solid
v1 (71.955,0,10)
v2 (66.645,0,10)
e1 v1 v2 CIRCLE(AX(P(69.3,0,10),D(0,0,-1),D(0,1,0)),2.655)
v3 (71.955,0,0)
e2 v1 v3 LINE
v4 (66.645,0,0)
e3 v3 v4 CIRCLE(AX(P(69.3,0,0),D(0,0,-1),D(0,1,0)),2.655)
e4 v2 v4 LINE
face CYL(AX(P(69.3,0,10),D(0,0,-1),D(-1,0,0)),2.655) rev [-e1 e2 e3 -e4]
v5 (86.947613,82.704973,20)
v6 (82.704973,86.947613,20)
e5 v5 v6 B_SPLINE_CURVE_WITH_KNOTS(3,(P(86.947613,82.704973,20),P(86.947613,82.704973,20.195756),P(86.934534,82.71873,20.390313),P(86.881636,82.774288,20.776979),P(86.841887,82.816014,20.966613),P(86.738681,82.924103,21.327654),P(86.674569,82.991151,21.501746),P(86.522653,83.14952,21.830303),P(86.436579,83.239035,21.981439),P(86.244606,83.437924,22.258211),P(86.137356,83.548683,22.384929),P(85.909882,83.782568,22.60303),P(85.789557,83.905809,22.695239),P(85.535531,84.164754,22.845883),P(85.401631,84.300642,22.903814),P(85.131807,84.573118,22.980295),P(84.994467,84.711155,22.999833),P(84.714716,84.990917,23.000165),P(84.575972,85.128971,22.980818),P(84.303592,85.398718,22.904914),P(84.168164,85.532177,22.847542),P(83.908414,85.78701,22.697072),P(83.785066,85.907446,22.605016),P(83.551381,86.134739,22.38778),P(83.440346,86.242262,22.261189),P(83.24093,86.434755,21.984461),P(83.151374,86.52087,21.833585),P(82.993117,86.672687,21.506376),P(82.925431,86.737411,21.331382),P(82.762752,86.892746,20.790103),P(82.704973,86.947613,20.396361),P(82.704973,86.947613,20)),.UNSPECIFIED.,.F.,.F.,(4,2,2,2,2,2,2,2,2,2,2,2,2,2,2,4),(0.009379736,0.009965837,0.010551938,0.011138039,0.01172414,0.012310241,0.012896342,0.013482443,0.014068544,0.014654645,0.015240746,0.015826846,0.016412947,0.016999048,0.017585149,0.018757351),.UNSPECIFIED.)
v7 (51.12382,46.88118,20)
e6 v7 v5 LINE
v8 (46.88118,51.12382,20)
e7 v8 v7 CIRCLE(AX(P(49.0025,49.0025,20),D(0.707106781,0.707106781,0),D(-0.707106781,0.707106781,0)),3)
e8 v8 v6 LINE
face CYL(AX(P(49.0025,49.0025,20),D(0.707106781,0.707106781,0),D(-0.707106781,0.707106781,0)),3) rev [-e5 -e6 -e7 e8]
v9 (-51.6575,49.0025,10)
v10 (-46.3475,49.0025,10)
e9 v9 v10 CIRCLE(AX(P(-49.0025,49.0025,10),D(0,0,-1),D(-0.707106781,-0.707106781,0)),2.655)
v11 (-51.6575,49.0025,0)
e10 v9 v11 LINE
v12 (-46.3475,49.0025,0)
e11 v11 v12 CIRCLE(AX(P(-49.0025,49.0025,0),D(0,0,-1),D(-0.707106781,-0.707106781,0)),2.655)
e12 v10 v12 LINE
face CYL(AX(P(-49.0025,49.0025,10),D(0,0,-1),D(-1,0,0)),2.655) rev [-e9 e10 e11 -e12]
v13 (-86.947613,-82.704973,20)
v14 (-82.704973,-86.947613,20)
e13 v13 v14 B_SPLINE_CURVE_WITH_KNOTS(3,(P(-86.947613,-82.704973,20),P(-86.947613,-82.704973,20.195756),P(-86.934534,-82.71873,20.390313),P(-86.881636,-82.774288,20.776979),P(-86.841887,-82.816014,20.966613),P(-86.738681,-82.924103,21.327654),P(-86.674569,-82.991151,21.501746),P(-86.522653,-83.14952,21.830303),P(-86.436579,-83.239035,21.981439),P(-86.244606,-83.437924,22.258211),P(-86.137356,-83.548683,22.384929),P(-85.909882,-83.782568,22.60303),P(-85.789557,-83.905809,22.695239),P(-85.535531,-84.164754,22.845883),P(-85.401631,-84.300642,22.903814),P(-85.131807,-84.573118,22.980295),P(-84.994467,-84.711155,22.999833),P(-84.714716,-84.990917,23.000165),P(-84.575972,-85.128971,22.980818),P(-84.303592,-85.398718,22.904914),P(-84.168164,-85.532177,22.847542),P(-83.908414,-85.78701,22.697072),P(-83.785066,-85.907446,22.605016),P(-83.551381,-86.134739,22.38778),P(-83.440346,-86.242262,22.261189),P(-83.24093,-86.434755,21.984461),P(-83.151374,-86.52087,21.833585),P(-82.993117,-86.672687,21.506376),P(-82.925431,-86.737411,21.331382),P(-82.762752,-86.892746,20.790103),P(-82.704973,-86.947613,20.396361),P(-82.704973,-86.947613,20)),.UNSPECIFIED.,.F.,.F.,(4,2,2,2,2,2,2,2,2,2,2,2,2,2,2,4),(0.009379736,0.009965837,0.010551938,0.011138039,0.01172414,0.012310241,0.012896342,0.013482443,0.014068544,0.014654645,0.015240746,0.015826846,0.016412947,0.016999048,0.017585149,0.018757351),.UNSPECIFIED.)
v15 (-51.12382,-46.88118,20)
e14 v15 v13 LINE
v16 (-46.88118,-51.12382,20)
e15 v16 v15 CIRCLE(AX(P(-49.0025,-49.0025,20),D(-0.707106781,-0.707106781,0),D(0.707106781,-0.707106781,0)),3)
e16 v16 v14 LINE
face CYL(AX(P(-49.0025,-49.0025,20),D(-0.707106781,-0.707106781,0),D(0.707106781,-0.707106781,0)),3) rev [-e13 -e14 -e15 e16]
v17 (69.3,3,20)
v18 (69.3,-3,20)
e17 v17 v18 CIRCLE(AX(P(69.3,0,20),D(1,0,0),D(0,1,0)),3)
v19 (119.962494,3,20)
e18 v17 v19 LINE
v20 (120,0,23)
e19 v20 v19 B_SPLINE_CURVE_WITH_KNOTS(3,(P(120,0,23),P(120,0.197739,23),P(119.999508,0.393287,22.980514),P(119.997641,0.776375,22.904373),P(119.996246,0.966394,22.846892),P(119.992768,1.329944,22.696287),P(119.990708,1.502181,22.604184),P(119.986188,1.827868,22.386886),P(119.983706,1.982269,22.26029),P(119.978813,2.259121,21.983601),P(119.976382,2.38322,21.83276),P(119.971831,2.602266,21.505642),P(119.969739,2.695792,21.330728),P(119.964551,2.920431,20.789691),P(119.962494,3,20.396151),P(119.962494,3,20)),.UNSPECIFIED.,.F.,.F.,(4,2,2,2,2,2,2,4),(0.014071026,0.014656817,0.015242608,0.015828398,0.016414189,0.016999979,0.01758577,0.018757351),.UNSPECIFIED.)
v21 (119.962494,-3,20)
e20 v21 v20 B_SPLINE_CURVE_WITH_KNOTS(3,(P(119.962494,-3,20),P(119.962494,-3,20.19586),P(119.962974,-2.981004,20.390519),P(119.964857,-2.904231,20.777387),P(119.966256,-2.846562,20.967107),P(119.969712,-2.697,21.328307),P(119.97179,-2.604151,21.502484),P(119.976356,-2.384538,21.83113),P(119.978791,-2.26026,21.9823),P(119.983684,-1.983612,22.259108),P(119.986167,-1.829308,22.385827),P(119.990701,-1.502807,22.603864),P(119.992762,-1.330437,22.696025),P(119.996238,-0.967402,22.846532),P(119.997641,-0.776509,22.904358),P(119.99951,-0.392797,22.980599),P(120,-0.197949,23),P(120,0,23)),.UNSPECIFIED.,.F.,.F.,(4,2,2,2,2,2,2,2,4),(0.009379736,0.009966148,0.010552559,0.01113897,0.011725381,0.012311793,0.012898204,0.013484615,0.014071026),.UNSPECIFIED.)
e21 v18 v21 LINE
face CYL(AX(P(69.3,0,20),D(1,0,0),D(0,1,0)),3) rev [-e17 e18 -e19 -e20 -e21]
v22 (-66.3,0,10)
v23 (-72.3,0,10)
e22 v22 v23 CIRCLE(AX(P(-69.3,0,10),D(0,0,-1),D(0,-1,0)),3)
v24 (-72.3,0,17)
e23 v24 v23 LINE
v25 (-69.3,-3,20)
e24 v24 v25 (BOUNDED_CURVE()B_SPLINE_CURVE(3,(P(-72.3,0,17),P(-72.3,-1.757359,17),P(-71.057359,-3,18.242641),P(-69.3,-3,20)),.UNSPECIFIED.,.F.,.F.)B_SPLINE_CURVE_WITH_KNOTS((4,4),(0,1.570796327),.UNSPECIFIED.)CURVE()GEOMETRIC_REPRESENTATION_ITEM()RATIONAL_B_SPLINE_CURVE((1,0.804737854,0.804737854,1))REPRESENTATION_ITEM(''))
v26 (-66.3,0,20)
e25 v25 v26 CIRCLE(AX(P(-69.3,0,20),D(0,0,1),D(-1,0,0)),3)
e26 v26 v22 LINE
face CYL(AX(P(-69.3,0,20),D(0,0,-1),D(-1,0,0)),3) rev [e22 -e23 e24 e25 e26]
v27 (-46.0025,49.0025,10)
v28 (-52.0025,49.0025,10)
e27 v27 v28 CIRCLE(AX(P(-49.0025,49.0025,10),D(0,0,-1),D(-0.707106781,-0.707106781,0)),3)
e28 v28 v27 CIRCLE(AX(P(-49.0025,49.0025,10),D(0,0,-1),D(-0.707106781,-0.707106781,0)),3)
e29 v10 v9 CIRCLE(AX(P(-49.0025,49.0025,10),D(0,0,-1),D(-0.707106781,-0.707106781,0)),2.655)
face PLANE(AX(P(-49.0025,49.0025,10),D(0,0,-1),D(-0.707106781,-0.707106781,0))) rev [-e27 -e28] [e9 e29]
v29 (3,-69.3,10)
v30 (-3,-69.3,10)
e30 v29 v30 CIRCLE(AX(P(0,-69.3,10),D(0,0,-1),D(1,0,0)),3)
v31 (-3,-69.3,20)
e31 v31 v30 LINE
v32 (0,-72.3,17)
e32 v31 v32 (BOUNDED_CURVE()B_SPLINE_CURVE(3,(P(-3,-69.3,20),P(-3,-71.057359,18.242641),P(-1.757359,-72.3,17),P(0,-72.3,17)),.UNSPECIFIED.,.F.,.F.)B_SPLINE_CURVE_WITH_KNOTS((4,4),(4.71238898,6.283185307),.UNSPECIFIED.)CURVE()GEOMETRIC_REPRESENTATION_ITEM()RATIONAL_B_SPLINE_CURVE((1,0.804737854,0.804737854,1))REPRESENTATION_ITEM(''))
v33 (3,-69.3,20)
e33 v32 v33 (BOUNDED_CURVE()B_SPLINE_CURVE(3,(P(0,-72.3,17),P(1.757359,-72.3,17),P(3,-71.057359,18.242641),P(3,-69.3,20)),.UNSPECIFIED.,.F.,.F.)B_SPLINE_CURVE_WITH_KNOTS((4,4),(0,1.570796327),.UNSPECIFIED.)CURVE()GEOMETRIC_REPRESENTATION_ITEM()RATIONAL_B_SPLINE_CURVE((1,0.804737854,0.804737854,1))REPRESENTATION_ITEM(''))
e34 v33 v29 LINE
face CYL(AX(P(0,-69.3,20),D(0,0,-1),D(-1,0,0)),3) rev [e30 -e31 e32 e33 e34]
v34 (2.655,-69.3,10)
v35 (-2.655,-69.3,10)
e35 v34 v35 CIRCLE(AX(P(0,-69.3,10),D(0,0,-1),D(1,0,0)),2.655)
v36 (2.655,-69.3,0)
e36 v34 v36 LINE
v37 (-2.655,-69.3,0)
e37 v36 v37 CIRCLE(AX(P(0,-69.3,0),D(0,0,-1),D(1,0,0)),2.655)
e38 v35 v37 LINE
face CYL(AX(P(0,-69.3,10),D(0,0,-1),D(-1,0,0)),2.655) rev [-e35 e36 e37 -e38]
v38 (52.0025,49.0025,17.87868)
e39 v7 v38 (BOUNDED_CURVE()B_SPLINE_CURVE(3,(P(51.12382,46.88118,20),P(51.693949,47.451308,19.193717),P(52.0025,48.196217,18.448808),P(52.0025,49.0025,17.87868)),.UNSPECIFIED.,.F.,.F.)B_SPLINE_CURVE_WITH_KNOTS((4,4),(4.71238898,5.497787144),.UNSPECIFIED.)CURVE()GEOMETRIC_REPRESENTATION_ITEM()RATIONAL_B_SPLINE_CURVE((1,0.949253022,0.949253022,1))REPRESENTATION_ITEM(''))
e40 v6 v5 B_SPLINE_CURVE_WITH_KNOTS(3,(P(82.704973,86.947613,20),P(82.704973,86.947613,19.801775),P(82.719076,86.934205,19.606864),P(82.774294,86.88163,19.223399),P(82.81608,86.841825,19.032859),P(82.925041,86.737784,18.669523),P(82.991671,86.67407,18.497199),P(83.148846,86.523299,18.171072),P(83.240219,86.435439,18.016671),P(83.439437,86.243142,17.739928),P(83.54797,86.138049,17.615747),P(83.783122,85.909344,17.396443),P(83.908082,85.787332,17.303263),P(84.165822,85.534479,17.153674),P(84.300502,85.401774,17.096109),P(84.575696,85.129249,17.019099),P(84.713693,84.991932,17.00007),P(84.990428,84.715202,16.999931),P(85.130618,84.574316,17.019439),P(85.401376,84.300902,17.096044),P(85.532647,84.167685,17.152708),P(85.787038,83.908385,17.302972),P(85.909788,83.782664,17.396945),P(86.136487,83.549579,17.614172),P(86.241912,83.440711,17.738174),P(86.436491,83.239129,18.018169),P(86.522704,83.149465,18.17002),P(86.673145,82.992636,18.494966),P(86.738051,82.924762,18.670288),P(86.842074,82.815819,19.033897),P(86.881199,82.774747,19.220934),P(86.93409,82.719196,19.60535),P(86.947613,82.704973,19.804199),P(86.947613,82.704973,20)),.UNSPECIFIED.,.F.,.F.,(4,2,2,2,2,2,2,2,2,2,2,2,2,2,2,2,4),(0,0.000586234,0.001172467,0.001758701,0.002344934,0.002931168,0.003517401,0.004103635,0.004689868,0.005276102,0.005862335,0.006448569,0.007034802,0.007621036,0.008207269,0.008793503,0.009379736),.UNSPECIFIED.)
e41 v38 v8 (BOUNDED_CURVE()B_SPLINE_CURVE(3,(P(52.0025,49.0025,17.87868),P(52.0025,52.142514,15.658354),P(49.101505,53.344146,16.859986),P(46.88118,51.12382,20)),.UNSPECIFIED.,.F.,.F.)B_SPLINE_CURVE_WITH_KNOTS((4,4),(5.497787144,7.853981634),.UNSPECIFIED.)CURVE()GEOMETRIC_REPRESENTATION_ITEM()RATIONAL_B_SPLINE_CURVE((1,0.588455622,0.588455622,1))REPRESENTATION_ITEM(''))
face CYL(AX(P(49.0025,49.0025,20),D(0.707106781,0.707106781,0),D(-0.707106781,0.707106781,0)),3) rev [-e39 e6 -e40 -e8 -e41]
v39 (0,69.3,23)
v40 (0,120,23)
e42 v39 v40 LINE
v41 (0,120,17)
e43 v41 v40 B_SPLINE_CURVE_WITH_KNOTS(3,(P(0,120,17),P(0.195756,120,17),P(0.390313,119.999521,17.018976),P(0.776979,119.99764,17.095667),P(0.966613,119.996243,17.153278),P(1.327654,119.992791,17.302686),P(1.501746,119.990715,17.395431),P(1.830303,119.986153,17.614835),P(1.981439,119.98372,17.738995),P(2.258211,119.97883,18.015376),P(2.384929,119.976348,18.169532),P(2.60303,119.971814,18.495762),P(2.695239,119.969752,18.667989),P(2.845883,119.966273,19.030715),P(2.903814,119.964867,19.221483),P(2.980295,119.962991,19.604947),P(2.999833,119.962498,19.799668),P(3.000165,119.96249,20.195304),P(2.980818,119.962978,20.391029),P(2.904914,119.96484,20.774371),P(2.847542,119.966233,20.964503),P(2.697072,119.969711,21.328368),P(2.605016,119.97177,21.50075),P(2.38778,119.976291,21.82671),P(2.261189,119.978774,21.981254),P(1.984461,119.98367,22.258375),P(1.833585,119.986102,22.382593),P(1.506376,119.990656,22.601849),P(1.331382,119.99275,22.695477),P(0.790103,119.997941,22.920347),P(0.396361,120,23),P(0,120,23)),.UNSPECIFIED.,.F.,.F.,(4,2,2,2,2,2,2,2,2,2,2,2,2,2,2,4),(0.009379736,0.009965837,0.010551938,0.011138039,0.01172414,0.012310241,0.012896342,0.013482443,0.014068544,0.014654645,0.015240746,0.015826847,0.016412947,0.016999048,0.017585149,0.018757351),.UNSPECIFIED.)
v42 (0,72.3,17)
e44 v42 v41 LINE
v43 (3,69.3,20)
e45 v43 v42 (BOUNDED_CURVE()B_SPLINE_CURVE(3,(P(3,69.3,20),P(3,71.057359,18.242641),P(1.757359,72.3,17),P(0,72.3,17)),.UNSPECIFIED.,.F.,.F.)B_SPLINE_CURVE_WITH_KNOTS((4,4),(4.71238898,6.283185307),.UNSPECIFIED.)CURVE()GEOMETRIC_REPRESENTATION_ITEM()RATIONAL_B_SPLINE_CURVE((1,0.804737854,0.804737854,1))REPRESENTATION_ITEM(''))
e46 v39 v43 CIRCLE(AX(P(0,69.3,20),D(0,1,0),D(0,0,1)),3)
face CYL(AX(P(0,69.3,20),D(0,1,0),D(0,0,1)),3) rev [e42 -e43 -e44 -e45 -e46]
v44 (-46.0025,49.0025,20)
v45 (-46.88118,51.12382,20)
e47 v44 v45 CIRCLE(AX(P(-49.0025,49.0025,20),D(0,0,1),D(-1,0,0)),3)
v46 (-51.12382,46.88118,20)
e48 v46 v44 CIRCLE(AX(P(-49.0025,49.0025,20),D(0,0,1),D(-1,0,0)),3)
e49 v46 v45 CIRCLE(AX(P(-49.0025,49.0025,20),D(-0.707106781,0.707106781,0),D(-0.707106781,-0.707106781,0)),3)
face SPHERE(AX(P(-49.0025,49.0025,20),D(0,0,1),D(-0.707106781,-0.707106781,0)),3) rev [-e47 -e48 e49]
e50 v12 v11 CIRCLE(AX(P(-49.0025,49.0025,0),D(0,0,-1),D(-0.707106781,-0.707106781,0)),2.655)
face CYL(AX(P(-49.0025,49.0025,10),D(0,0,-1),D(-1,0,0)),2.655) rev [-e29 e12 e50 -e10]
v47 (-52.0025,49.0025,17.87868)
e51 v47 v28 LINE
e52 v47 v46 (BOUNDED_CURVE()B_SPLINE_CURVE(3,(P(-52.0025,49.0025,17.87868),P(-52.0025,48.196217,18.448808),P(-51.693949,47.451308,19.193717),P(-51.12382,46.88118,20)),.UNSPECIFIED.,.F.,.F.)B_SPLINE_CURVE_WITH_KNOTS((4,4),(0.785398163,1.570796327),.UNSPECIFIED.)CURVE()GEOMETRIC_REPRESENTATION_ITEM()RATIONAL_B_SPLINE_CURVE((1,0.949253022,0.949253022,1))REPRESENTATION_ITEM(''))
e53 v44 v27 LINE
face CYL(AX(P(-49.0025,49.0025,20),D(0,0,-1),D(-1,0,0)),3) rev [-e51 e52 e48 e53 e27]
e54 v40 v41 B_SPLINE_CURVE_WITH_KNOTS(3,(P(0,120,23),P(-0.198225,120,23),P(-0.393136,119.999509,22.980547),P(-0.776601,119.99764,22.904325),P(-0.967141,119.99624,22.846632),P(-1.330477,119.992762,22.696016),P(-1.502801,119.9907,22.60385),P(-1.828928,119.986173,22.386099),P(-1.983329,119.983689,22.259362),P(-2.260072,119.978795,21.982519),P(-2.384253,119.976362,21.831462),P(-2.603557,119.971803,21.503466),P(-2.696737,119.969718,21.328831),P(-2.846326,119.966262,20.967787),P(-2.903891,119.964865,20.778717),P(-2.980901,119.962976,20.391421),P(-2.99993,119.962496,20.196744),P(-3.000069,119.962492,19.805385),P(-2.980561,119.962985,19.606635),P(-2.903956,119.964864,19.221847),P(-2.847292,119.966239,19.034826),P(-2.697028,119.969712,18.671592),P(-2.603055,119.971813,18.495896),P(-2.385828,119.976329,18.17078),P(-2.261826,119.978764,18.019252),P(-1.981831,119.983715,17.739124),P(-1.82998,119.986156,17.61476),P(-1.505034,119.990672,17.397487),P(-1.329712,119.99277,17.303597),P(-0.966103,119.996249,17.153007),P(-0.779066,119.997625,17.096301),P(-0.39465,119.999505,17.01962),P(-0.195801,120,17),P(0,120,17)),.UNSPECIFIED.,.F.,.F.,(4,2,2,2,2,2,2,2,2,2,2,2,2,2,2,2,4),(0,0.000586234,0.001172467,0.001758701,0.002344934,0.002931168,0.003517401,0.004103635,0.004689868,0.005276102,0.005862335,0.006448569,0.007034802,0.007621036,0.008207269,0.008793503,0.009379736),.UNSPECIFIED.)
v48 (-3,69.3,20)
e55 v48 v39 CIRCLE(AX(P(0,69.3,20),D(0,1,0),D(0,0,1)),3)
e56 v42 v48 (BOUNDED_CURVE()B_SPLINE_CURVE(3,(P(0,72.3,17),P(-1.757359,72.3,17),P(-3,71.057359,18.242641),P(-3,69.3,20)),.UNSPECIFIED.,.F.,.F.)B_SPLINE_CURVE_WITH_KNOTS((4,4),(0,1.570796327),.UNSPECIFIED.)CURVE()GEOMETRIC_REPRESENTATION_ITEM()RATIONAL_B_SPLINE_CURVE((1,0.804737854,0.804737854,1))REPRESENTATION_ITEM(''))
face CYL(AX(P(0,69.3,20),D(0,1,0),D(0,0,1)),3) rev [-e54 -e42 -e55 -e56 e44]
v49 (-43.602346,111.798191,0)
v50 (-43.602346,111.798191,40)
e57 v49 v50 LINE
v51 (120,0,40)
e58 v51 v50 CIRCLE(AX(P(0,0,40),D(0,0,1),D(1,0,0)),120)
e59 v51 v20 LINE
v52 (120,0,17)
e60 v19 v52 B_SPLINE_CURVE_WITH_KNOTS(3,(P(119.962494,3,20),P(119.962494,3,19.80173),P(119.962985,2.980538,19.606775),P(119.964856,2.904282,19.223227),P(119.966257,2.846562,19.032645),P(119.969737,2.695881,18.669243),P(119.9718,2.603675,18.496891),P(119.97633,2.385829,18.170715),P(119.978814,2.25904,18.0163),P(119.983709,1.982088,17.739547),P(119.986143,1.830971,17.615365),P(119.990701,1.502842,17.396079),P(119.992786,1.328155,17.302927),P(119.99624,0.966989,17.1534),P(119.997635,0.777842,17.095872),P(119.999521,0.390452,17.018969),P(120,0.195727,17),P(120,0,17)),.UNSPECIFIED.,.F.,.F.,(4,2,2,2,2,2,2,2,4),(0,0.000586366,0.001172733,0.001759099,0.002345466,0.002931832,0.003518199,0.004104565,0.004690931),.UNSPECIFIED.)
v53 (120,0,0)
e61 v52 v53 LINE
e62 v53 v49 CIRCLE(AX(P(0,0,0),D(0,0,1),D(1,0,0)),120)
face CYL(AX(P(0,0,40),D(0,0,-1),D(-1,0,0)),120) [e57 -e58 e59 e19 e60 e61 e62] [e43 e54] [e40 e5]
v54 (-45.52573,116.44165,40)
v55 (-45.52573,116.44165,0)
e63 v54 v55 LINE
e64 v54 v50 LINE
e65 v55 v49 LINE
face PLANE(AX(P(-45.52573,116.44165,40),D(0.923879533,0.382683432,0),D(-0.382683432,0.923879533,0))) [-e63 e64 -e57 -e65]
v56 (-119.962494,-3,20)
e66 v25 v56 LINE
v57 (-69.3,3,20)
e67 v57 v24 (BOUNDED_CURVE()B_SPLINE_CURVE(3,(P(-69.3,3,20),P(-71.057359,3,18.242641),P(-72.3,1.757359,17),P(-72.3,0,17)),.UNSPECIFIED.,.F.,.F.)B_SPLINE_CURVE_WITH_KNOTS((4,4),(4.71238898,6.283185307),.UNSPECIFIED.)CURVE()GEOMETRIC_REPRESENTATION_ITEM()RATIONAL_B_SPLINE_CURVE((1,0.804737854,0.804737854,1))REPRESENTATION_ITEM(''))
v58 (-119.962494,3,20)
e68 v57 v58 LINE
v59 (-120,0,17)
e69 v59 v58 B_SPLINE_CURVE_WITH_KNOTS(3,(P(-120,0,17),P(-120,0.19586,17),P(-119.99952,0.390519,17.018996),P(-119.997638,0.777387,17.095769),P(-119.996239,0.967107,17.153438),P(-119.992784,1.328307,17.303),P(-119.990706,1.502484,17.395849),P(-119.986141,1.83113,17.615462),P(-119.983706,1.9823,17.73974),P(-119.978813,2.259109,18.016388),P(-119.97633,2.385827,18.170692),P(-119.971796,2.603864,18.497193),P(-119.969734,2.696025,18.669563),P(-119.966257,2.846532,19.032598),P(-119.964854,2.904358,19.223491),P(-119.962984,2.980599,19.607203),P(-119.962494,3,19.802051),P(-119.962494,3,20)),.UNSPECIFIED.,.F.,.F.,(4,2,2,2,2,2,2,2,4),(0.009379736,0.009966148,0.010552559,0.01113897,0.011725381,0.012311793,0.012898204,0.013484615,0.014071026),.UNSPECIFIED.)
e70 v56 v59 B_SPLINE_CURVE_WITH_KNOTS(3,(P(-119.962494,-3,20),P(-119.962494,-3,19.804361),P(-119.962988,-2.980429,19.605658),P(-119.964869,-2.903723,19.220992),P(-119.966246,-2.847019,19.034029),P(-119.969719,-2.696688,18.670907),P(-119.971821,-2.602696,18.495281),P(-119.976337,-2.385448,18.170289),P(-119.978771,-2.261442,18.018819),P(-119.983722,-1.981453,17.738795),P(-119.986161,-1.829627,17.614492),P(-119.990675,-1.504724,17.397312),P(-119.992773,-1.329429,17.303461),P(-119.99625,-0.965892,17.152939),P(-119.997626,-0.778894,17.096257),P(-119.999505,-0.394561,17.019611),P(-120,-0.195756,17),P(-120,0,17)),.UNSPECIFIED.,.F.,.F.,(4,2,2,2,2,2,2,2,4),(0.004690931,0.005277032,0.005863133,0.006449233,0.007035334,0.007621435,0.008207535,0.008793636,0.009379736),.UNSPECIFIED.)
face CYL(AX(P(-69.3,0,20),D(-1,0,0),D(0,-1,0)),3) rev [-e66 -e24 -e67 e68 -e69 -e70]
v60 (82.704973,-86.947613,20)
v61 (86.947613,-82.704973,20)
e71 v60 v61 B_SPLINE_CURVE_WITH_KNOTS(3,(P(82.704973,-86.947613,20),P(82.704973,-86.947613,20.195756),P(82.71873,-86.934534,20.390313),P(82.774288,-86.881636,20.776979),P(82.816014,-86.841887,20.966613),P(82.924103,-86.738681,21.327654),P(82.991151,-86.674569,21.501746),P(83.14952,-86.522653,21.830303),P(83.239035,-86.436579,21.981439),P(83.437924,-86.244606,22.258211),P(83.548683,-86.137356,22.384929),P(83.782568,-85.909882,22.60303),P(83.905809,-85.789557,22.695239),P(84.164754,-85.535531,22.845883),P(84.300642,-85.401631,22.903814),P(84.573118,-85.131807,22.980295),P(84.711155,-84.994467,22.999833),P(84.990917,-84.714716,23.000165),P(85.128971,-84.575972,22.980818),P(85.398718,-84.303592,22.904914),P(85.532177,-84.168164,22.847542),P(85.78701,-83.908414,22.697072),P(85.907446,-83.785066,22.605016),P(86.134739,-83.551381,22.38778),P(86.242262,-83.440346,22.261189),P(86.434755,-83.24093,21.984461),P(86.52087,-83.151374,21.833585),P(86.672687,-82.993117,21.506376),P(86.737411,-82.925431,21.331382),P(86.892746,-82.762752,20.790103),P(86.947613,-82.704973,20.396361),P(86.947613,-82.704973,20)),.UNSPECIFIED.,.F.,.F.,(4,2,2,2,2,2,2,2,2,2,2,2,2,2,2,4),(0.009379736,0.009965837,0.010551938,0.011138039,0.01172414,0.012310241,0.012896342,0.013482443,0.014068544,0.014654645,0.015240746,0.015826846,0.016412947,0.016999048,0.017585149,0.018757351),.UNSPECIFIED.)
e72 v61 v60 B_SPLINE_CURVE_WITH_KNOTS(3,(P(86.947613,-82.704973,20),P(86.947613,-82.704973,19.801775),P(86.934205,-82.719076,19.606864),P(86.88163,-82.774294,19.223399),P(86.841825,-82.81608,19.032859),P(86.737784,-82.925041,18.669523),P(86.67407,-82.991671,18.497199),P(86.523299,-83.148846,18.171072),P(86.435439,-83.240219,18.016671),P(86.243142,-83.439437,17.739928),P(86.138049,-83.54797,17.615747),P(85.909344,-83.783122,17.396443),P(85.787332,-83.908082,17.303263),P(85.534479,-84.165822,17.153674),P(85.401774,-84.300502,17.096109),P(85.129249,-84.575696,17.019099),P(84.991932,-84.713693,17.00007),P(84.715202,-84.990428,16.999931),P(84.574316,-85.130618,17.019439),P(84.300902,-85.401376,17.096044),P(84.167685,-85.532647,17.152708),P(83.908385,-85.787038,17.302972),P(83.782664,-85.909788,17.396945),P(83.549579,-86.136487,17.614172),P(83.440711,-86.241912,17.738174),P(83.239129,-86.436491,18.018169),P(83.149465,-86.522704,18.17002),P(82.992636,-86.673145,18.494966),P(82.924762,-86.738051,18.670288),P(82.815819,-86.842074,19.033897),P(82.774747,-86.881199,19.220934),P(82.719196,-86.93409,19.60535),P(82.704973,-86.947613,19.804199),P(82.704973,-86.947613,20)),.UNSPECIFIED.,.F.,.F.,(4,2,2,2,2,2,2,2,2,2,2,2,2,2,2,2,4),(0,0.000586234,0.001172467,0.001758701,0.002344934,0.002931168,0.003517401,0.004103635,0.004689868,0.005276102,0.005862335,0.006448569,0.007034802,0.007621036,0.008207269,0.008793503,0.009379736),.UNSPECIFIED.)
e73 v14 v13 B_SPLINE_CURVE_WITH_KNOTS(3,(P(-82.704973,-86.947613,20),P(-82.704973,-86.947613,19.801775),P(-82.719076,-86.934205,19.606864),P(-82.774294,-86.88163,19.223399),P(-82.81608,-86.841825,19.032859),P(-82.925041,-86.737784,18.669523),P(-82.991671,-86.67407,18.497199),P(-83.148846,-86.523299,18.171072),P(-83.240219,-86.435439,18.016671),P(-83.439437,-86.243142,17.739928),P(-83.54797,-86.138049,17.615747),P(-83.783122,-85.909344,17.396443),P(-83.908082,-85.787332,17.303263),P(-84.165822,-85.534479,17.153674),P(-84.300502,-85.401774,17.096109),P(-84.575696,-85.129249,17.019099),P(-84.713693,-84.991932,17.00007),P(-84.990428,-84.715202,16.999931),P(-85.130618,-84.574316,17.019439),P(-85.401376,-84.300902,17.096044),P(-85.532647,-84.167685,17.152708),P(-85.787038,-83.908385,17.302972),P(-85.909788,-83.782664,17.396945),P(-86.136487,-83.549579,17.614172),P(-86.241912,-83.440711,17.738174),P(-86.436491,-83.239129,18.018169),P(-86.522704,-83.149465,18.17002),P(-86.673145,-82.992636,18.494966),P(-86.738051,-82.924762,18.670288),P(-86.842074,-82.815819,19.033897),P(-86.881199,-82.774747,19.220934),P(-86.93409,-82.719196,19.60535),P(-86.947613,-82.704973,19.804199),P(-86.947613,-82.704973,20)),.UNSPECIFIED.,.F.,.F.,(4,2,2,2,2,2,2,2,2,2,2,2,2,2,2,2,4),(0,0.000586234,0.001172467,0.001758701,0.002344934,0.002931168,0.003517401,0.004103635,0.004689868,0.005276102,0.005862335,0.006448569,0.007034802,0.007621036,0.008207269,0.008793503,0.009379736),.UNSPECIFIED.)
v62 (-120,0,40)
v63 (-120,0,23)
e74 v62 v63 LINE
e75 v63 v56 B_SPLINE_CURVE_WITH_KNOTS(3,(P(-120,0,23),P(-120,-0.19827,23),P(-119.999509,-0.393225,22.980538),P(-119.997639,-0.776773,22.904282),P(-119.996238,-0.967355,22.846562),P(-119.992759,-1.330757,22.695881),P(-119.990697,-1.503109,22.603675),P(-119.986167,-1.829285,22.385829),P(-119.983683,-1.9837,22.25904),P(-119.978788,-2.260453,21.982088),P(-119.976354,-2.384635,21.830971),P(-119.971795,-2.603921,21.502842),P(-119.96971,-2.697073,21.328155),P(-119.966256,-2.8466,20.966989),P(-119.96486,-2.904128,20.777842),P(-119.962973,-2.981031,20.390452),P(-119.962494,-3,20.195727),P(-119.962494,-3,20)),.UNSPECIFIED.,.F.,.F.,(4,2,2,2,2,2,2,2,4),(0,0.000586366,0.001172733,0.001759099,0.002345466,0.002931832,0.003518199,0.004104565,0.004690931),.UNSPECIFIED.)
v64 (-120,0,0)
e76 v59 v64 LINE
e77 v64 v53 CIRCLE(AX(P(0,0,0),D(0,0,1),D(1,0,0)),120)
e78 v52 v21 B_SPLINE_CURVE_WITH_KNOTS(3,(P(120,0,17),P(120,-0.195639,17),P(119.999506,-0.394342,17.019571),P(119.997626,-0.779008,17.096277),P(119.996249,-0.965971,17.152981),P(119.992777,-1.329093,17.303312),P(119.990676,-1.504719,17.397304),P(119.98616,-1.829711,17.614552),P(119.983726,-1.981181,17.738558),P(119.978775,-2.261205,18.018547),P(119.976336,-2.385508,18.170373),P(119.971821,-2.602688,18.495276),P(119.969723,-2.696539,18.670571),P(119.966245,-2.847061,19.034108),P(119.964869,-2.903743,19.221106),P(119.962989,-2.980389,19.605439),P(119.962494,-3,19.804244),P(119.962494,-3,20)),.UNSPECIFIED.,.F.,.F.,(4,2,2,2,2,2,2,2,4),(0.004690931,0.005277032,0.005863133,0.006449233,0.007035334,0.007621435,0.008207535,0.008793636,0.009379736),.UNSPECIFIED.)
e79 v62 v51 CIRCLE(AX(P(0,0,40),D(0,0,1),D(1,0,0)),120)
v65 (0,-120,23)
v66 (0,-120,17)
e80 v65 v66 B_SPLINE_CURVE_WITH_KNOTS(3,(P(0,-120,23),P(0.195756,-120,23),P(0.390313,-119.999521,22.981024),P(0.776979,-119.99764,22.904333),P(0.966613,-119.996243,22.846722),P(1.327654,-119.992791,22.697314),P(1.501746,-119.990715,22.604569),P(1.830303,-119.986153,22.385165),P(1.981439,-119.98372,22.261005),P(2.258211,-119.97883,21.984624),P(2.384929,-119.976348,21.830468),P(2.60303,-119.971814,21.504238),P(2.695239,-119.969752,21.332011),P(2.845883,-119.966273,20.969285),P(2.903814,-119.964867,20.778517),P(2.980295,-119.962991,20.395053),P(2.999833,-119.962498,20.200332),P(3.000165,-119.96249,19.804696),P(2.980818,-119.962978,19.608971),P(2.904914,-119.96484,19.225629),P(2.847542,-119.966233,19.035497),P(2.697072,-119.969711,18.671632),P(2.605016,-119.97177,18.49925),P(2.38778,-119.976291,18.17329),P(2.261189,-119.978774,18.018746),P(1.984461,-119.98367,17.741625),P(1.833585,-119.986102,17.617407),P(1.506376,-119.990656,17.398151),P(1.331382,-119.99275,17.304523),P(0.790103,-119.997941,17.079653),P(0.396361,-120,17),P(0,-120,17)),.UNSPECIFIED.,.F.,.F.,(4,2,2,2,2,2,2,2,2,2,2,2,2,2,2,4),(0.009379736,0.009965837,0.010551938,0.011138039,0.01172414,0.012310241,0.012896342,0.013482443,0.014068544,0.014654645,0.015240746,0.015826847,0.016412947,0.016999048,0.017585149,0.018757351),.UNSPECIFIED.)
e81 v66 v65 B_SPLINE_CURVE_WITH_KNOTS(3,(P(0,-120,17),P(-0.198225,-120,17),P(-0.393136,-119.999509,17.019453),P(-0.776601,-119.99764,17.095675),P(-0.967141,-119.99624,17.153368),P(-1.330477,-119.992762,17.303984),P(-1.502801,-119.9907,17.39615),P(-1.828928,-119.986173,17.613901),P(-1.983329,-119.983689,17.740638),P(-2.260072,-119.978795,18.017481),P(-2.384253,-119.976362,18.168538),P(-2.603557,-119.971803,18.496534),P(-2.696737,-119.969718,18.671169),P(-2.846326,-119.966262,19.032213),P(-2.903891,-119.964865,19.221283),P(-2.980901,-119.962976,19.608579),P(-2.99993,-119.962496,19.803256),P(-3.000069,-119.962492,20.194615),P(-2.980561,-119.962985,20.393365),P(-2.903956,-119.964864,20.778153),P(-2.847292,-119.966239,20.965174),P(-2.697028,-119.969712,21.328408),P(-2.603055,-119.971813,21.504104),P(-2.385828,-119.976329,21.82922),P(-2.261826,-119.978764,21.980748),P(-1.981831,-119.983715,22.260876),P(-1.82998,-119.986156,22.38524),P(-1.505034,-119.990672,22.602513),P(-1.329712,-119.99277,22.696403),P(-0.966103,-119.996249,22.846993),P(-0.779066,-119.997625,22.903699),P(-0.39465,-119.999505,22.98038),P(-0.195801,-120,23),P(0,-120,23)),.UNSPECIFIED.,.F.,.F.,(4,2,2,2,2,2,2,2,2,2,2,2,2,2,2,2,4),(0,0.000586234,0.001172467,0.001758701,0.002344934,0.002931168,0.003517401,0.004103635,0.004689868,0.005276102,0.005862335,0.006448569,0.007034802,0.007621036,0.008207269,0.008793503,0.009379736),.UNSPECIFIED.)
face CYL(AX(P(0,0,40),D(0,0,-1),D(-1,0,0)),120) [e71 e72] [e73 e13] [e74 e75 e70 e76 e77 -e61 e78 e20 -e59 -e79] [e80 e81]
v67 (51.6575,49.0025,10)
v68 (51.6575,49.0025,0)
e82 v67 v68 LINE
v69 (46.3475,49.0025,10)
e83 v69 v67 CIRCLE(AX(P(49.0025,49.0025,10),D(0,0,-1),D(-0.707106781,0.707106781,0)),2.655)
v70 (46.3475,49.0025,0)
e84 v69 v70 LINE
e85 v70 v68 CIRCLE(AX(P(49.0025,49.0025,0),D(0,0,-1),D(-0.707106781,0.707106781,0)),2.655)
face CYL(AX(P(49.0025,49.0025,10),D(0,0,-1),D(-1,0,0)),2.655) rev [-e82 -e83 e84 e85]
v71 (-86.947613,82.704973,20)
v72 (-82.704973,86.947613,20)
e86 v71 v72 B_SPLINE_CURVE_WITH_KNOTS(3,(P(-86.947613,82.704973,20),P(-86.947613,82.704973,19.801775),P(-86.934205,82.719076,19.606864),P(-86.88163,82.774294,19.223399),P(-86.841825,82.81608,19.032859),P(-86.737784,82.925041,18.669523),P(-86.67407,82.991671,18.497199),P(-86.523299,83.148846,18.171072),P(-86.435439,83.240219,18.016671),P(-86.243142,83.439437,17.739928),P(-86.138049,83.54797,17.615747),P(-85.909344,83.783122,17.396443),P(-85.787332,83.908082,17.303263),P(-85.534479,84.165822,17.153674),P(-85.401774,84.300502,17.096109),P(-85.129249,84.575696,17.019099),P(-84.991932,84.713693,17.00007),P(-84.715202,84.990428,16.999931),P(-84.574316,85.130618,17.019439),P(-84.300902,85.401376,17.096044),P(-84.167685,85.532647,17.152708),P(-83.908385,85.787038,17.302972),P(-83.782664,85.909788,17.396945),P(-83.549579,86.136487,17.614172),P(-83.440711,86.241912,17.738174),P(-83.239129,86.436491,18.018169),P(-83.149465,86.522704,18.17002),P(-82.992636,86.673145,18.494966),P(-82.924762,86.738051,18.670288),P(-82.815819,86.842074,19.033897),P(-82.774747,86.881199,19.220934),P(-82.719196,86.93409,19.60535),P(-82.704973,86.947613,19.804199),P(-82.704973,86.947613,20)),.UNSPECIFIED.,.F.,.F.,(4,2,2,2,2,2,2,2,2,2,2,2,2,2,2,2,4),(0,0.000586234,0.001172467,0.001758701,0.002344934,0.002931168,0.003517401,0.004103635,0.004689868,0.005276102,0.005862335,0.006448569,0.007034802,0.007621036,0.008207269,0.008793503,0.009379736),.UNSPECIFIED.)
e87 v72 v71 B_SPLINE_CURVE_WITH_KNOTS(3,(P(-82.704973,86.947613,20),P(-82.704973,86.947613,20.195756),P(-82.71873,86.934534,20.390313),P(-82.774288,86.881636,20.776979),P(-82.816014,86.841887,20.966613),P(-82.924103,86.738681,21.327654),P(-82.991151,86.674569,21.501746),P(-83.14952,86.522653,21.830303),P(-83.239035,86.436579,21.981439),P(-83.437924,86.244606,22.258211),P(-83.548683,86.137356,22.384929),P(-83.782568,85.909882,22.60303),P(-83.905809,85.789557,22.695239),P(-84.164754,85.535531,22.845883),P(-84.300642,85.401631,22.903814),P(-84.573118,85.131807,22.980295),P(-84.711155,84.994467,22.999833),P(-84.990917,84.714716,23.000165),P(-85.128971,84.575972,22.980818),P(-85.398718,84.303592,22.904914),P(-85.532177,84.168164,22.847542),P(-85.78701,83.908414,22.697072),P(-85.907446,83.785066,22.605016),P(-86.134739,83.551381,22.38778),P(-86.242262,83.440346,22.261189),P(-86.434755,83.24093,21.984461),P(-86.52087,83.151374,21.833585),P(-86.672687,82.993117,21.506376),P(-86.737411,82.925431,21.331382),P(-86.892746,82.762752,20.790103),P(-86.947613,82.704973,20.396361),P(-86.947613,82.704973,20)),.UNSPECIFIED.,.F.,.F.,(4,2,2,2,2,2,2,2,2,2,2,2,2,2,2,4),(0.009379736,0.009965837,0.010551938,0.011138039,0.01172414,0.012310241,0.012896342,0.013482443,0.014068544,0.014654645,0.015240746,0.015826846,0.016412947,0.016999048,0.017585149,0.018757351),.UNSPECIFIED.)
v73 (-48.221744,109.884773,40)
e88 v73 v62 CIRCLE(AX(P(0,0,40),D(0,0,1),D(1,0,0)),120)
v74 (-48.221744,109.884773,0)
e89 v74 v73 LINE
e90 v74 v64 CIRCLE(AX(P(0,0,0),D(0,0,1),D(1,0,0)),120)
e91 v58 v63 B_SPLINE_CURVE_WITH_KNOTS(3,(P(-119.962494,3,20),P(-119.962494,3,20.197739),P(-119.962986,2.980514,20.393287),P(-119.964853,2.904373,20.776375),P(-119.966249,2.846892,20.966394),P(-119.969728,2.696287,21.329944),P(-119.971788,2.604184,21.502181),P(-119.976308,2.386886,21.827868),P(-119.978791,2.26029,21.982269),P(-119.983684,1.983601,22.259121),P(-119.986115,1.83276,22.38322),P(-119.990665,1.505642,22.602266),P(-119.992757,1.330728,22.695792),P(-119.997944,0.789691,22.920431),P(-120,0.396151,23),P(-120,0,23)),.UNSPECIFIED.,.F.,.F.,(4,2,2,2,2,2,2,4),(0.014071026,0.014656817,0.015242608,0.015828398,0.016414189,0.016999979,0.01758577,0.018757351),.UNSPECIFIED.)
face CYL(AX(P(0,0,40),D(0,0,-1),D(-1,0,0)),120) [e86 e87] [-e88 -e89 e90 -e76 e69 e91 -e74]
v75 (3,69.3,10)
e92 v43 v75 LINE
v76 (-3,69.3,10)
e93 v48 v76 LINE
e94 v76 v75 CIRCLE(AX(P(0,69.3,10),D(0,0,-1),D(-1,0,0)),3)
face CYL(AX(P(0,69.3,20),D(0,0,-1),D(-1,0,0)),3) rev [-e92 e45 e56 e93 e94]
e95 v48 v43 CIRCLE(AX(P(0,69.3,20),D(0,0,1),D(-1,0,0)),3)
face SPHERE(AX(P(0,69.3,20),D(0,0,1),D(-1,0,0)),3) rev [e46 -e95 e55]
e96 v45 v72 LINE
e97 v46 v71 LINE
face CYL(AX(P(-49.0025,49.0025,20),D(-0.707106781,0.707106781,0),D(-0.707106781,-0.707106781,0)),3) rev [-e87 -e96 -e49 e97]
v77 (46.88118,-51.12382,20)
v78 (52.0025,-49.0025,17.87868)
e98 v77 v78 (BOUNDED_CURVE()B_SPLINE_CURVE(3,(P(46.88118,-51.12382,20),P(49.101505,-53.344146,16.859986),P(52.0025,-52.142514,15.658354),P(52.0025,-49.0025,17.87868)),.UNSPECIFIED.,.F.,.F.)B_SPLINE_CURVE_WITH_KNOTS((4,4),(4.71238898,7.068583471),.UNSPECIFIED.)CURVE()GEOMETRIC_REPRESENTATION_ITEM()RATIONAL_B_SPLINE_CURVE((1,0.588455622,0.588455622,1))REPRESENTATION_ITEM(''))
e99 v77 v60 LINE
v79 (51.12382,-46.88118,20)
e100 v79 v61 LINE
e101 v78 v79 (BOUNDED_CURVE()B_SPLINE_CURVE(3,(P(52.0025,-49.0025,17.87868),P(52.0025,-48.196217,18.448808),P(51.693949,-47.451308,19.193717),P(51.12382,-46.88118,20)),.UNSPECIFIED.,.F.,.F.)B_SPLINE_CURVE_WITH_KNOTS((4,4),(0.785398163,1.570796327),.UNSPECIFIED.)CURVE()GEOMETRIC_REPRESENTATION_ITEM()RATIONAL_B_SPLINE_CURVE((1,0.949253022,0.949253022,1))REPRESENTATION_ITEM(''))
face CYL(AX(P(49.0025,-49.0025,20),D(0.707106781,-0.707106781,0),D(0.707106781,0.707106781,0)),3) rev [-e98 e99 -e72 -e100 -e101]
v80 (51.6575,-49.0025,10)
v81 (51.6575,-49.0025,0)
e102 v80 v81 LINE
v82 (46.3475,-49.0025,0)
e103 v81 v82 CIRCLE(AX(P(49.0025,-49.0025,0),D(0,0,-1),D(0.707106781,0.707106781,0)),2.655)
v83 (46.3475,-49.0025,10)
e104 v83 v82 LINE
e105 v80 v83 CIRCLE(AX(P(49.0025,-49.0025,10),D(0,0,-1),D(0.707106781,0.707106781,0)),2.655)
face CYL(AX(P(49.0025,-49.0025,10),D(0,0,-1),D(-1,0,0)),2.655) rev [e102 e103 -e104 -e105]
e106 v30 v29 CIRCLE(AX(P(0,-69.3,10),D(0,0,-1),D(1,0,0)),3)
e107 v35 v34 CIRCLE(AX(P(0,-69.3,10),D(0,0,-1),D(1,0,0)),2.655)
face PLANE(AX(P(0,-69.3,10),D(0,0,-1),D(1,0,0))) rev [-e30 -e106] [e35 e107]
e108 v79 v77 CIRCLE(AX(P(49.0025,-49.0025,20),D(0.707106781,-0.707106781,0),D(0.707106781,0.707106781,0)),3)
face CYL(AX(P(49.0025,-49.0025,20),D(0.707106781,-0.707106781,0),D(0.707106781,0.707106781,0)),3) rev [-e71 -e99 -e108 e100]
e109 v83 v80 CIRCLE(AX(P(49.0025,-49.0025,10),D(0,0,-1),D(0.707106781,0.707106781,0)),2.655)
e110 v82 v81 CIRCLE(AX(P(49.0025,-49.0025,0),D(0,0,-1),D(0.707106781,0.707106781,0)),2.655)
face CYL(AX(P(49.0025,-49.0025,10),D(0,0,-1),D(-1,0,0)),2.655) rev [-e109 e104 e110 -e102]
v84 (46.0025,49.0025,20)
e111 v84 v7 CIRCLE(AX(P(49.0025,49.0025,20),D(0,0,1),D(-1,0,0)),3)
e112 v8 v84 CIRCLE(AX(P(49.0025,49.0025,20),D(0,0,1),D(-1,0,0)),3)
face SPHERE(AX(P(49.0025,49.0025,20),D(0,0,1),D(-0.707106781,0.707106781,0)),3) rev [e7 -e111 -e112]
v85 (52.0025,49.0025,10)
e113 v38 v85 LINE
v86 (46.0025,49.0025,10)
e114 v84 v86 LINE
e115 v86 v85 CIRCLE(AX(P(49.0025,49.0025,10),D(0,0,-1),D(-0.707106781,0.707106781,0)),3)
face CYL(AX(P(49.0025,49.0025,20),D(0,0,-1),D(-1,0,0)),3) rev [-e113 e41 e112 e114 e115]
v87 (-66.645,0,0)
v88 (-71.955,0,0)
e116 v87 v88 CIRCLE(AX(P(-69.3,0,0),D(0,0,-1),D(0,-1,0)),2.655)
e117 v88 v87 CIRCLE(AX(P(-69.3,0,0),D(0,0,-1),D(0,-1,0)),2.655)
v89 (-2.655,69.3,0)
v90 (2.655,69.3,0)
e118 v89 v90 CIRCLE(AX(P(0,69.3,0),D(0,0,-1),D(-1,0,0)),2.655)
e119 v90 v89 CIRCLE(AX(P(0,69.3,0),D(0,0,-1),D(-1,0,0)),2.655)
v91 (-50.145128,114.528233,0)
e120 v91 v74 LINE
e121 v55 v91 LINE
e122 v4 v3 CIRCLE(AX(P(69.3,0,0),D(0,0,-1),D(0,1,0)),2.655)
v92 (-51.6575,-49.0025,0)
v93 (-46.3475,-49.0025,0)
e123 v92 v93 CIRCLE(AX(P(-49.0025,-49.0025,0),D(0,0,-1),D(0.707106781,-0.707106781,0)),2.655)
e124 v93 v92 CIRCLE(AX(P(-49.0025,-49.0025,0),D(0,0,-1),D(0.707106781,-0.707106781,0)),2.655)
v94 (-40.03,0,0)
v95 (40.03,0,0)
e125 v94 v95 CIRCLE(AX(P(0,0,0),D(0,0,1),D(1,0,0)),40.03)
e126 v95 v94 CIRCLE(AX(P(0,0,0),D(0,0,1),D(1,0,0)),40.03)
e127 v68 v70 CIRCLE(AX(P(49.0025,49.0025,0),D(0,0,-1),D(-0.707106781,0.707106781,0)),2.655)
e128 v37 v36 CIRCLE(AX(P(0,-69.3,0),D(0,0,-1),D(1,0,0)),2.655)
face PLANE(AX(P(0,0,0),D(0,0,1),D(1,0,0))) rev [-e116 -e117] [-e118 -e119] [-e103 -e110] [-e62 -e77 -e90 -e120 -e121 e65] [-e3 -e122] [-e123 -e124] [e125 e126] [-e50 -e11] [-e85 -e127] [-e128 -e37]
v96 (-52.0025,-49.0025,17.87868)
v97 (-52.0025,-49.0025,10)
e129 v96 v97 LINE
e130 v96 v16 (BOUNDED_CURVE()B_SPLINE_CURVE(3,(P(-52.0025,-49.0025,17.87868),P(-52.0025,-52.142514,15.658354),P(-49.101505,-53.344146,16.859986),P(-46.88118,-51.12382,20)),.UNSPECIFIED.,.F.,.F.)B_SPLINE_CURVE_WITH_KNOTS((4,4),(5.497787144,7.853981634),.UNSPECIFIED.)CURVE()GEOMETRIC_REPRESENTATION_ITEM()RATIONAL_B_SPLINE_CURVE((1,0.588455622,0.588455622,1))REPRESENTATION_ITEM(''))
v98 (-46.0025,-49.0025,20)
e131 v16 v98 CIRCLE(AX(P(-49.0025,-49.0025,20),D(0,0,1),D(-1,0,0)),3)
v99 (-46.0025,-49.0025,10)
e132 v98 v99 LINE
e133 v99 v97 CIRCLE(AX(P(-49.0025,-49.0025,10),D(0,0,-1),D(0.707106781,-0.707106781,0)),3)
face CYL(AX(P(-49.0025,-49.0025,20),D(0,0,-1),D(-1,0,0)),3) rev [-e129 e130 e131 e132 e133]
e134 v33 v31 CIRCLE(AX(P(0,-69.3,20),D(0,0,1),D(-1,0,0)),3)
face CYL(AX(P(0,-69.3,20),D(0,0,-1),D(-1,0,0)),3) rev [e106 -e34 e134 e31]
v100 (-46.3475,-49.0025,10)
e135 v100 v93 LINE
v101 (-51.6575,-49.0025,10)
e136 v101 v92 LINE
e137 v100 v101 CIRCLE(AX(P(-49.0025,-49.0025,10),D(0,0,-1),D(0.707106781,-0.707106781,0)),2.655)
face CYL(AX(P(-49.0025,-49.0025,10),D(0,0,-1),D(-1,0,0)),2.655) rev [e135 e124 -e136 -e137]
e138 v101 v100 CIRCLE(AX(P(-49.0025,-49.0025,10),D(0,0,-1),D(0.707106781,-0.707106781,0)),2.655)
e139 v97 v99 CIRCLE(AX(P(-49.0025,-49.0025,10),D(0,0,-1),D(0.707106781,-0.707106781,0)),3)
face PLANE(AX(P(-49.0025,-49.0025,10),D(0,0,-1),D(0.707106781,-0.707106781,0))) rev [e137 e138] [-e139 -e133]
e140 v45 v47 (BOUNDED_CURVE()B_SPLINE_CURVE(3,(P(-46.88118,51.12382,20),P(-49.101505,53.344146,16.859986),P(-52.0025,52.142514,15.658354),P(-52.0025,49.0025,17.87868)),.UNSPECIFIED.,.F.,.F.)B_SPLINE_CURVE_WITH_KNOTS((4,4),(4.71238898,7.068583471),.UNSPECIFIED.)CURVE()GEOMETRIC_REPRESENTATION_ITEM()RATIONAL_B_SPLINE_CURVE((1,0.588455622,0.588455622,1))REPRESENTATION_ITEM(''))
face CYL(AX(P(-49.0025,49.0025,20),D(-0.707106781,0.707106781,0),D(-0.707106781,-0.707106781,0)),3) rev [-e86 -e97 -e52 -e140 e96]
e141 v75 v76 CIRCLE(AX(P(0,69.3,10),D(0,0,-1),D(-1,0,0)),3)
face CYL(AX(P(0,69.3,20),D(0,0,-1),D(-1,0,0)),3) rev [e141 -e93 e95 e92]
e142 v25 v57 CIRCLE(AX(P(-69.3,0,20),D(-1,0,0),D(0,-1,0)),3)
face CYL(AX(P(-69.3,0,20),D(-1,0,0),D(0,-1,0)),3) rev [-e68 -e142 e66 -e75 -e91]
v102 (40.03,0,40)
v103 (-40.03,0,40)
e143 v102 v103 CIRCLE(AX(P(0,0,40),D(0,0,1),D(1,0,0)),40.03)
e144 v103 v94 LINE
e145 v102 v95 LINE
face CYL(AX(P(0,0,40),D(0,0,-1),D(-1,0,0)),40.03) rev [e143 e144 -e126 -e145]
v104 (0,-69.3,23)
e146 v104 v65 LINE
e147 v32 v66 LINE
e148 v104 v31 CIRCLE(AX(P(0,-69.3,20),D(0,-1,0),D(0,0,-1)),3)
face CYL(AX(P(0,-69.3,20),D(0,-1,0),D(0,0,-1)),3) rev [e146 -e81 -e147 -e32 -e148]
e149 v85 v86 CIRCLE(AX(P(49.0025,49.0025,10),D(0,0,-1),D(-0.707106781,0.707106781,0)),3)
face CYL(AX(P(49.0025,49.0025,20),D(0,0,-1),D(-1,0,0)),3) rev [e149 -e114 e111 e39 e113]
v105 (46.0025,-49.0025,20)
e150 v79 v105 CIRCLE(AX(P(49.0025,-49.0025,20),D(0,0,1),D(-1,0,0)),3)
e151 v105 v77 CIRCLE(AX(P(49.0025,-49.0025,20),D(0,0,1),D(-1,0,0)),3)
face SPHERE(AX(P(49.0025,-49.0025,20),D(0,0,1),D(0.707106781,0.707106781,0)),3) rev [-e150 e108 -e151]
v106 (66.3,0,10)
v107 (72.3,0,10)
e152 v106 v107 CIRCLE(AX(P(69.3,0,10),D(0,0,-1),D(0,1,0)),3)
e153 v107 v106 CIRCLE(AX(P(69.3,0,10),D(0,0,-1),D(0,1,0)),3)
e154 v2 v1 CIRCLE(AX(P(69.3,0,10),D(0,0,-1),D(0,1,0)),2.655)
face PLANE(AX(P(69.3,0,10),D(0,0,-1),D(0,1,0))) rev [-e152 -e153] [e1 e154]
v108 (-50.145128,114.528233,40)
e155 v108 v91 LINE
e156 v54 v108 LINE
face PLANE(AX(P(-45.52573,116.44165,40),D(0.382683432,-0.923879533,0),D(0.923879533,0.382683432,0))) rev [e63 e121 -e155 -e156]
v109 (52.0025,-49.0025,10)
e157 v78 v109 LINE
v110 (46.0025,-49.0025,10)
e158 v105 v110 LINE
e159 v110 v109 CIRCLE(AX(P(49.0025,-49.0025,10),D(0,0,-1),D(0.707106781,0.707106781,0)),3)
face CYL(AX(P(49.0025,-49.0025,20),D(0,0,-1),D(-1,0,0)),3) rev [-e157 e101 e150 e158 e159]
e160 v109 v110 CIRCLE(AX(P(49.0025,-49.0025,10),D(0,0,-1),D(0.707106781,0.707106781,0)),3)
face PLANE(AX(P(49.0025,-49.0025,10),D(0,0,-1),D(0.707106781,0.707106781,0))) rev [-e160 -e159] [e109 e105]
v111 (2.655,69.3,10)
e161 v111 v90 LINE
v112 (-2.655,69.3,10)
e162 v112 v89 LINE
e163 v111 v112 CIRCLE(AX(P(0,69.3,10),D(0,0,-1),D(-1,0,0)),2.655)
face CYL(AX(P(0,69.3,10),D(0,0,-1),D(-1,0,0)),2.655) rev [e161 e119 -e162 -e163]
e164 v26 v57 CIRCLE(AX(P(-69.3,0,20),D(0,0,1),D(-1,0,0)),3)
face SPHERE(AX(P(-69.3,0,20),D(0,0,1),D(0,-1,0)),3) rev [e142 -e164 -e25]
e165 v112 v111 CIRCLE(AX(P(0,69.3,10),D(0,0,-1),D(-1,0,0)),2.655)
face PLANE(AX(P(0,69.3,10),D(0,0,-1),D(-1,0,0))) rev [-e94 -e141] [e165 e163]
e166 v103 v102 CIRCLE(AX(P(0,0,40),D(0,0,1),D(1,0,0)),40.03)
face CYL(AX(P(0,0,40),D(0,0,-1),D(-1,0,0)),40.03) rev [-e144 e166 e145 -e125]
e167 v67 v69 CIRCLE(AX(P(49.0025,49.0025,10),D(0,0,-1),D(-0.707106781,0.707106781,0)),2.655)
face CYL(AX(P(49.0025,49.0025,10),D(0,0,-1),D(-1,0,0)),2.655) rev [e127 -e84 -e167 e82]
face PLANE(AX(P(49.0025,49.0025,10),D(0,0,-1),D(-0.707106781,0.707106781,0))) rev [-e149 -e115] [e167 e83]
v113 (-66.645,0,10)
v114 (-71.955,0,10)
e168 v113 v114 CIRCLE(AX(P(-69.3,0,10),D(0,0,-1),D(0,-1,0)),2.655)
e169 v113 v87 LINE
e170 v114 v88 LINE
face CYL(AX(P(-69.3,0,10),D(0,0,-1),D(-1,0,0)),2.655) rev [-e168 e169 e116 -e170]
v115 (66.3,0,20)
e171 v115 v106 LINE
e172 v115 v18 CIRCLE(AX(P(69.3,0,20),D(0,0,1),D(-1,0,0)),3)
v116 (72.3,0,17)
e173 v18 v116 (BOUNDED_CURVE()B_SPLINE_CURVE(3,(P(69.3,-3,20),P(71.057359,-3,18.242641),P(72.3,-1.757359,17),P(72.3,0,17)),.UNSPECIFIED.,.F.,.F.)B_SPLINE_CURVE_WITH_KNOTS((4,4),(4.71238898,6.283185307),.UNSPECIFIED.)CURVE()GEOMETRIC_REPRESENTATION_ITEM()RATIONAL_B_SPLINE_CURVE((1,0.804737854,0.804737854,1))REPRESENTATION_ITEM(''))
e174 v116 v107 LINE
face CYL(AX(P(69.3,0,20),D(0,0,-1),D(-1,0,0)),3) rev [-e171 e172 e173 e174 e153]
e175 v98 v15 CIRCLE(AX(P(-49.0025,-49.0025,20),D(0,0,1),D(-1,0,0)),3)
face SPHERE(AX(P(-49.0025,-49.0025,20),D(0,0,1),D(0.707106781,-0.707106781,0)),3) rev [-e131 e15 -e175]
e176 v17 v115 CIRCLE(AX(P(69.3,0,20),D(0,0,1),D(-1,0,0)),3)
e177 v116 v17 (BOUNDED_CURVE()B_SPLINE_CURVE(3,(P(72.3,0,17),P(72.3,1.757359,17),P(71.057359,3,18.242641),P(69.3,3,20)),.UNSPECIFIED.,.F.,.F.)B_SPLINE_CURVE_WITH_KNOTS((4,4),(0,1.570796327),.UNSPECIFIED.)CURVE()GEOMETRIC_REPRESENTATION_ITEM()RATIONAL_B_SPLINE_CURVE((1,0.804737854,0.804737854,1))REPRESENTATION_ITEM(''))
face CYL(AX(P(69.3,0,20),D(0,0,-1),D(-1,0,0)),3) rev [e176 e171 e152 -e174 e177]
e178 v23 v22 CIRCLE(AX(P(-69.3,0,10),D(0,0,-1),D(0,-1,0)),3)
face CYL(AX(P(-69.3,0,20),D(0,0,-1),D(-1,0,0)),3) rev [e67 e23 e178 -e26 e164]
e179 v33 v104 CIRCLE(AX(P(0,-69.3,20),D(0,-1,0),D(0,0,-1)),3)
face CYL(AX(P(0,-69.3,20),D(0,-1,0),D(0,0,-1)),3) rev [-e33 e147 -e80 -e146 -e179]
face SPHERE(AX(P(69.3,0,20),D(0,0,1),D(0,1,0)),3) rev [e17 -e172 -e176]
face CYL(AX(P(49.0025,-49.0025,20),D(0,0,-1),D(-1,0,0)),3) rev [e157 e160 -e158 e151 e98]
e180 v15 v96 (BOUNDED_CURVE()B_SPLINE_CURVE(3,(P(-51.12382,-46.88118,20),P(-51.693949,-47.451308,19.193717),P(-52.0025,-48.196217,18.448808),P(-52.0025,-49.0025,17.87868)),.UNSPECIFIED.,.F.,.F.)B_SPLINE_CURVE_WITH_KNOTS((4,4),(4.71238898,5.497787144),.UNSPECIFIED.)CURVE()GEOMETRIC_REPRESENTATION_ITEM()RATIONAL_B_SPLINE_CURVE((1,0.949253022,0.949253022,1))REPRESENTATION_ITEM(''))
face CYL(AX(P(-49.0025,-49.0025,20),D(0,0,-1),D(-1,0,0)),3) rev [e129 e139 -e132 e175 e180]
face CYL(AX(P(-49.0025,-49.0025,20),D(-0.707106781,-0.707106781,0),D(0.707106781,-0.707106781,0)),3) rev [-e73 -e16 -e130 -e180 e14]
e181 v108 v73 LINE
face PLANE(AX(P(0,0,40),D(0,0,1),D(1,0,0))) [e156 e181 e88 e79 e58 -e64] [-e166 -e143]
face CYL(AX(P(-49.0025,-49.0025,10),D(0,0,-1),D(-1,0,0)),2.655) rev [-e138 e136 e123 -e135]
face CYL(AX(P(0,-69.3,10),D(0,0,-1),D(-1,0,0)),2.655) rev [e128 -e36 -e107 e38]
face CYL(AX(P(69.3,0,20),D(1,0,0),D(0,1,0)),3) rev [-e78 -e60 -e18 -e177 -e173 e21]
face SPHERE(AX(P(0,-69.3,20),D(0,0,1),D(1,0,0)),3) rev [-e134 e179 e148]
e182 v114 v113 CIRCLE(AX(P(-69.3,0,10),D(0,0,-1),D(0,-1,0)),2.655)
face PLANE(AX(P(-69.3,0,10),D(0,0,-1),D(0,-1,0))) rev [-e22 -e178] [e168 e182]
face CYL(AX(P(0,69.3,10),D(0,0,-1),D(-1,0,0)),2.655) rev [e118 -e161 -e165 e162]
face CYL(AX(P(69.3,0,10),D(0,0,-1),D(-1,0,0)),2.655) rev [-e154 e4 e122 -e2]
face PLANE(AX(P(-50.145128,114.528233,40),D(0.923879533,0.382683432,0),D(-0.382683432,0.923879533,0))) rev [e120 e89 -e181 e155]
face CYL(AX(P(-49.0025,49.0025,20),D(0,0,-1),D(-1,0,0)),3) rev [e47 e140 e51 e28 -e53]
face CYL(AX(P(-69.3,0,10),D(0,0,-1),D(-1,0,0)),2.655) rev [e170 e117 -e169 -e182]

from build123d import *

# Parameters (mm, degrees)
SKETCH1_R           = 120
SKETCH1_R_2         = 40.03000000000001
BOSS_EXTRUDE1_DEPTH = 40
SKETCH2_R           = 2.654999999999998
CUT_EXTRUDE1_DEPTH  = 10
SKETCH3_R           = 3.000000000000001
CUT_EXTRUDE3_DEPTH  = 10
SKETCH6_R           = 3.000000000000003
CUT_EXTRUDE4_DEPTH  = 50.7
CIRPATTERN1_COUNT   = 8
BOSS_EXTRUDE2_DEPTH = 40


with BuildPart() as part:
    # Sketch1 → Boss-Extrude1 (new body)
    with BuildSketch(Plane.XY):
        Circle(SKETCH1_R)
        Circle(SKETCH1_R_2, mode=Mode.SUBTRACT)
    extrude(amount=BOSS_EXTRUDE1_DEPTH)

    # Sketch2 → Cut-Extrude1 (cut)
    with BuildSketch(Plane(origin=(0, 0, 0), x_dir=(-1, 0, 0), z_dir=(0, 0, -1))):
        with Locations((0, 69.3)):
            Circle(SKETCH2_R)
    cut_extrude1 = extrude(amount=-CUT_EXTRUDE1_DEPTH, mode=Mode.SUBTRACT)

    # Sketch3 → Cut-Extrude3 (cut)
    with BuildSketch(Plane(origin=(0, 0, 10), x_dir=(-1, 0, 0), z_dir=(0, 0, -1))):
        with Locations((0, 69.3)):
            Circle(SKETCH3_R)
    cut_extrude3 = extrude(amount=-CUT_EXTRUDE3_DEPTH, mode=Mode.SUBTRACT)

    # Sketch5 → Cut-Revolve1 (revolve, cut)
    with BuildSketch(Plane(origin=(0, 0, 20), x_dir=(-1, 0, 0), z_dir=(0, 0, -1))):
        with BuildLine():
            Line((0, 72.3), (0, 66.3))
            ThreePointArc((0, 66.3), (3, 69.3), (0, 72.3))
        make_face()
    cut_revolve1 = revolve(axis=Axis((0, 72.3, 20), (0, -1, 0)), mode=Mode.SUBTRACT)

    # Sketch6 → Cut-Extrude4 (cut)
    with BuildSketch(Plane(origin=(0, 120, 0), x_dir=(1, 0, 0), z_dir=(0, 1, 0))):
        with Locations(Location((0, -20, 0), (0, 0, 270))):
            Circle(SKETCH6_R)
    cut_extrude4 = extrude(amount=-CUT_EXTRUDE4_DEPTH, mode=Mode.SUBTRACT)

    # CirPattern1: Cut-Extrude1, Cut-Extrude3, Cut-Revolve1, Cut-Extrude4 ×8 about axis
    cirpattern1_axis = Axis((-6.08e-14, 1.3e-16, 0), (0, 0, 1))
    add([cut_extrude1.rotate(cirpattern1_axis, i * 360 / CIRPATTERN1_COUNT) for i in range(1, CIRPATTERN1_COUNT)], mode=Mode.SUBTRACT)
    add([cut_extrude3.rotate(cirpattern1_axis, i * 360 / CIRPATTERN1_COUNT) for i in range(1, CIRPATTERN1_COUNT)], mode=Mode.SUBTRACT)
    add([cut_revolve1.rotate(cirpattern1_axis, i * 360 / CIRPATTERN1_COUNT) for i in range(1, CIRPATTERN1_COUNT)], mode=Mode.SUBTRACT)
    add([cut_extrude4.rotate(cirpattern1_axis, i * 360 / CIRPATTERN1_COUNT) for i in range(1, CIRPATTERN1_COUNT)], mode=Mode.SUBTRACT)

    # Sketch7 → Boss-Extrude2 (add)
    with BuildSketch(Plane(origin=(0, 0, 0), x_dir=(-1, 0, 0), z_dir=(0, 0, -1))):
        Polygon((45.525730214358006, 116.44165014482351), (50.14512787691445, 114.52823298299805), (47.7461408529735, 108.73656597384273), (43.126743190417045, 110.6499831356682), align=None)
    extrude(amount=-BOSS_EXTRUDE2_DEPTH)


solid = part.part
